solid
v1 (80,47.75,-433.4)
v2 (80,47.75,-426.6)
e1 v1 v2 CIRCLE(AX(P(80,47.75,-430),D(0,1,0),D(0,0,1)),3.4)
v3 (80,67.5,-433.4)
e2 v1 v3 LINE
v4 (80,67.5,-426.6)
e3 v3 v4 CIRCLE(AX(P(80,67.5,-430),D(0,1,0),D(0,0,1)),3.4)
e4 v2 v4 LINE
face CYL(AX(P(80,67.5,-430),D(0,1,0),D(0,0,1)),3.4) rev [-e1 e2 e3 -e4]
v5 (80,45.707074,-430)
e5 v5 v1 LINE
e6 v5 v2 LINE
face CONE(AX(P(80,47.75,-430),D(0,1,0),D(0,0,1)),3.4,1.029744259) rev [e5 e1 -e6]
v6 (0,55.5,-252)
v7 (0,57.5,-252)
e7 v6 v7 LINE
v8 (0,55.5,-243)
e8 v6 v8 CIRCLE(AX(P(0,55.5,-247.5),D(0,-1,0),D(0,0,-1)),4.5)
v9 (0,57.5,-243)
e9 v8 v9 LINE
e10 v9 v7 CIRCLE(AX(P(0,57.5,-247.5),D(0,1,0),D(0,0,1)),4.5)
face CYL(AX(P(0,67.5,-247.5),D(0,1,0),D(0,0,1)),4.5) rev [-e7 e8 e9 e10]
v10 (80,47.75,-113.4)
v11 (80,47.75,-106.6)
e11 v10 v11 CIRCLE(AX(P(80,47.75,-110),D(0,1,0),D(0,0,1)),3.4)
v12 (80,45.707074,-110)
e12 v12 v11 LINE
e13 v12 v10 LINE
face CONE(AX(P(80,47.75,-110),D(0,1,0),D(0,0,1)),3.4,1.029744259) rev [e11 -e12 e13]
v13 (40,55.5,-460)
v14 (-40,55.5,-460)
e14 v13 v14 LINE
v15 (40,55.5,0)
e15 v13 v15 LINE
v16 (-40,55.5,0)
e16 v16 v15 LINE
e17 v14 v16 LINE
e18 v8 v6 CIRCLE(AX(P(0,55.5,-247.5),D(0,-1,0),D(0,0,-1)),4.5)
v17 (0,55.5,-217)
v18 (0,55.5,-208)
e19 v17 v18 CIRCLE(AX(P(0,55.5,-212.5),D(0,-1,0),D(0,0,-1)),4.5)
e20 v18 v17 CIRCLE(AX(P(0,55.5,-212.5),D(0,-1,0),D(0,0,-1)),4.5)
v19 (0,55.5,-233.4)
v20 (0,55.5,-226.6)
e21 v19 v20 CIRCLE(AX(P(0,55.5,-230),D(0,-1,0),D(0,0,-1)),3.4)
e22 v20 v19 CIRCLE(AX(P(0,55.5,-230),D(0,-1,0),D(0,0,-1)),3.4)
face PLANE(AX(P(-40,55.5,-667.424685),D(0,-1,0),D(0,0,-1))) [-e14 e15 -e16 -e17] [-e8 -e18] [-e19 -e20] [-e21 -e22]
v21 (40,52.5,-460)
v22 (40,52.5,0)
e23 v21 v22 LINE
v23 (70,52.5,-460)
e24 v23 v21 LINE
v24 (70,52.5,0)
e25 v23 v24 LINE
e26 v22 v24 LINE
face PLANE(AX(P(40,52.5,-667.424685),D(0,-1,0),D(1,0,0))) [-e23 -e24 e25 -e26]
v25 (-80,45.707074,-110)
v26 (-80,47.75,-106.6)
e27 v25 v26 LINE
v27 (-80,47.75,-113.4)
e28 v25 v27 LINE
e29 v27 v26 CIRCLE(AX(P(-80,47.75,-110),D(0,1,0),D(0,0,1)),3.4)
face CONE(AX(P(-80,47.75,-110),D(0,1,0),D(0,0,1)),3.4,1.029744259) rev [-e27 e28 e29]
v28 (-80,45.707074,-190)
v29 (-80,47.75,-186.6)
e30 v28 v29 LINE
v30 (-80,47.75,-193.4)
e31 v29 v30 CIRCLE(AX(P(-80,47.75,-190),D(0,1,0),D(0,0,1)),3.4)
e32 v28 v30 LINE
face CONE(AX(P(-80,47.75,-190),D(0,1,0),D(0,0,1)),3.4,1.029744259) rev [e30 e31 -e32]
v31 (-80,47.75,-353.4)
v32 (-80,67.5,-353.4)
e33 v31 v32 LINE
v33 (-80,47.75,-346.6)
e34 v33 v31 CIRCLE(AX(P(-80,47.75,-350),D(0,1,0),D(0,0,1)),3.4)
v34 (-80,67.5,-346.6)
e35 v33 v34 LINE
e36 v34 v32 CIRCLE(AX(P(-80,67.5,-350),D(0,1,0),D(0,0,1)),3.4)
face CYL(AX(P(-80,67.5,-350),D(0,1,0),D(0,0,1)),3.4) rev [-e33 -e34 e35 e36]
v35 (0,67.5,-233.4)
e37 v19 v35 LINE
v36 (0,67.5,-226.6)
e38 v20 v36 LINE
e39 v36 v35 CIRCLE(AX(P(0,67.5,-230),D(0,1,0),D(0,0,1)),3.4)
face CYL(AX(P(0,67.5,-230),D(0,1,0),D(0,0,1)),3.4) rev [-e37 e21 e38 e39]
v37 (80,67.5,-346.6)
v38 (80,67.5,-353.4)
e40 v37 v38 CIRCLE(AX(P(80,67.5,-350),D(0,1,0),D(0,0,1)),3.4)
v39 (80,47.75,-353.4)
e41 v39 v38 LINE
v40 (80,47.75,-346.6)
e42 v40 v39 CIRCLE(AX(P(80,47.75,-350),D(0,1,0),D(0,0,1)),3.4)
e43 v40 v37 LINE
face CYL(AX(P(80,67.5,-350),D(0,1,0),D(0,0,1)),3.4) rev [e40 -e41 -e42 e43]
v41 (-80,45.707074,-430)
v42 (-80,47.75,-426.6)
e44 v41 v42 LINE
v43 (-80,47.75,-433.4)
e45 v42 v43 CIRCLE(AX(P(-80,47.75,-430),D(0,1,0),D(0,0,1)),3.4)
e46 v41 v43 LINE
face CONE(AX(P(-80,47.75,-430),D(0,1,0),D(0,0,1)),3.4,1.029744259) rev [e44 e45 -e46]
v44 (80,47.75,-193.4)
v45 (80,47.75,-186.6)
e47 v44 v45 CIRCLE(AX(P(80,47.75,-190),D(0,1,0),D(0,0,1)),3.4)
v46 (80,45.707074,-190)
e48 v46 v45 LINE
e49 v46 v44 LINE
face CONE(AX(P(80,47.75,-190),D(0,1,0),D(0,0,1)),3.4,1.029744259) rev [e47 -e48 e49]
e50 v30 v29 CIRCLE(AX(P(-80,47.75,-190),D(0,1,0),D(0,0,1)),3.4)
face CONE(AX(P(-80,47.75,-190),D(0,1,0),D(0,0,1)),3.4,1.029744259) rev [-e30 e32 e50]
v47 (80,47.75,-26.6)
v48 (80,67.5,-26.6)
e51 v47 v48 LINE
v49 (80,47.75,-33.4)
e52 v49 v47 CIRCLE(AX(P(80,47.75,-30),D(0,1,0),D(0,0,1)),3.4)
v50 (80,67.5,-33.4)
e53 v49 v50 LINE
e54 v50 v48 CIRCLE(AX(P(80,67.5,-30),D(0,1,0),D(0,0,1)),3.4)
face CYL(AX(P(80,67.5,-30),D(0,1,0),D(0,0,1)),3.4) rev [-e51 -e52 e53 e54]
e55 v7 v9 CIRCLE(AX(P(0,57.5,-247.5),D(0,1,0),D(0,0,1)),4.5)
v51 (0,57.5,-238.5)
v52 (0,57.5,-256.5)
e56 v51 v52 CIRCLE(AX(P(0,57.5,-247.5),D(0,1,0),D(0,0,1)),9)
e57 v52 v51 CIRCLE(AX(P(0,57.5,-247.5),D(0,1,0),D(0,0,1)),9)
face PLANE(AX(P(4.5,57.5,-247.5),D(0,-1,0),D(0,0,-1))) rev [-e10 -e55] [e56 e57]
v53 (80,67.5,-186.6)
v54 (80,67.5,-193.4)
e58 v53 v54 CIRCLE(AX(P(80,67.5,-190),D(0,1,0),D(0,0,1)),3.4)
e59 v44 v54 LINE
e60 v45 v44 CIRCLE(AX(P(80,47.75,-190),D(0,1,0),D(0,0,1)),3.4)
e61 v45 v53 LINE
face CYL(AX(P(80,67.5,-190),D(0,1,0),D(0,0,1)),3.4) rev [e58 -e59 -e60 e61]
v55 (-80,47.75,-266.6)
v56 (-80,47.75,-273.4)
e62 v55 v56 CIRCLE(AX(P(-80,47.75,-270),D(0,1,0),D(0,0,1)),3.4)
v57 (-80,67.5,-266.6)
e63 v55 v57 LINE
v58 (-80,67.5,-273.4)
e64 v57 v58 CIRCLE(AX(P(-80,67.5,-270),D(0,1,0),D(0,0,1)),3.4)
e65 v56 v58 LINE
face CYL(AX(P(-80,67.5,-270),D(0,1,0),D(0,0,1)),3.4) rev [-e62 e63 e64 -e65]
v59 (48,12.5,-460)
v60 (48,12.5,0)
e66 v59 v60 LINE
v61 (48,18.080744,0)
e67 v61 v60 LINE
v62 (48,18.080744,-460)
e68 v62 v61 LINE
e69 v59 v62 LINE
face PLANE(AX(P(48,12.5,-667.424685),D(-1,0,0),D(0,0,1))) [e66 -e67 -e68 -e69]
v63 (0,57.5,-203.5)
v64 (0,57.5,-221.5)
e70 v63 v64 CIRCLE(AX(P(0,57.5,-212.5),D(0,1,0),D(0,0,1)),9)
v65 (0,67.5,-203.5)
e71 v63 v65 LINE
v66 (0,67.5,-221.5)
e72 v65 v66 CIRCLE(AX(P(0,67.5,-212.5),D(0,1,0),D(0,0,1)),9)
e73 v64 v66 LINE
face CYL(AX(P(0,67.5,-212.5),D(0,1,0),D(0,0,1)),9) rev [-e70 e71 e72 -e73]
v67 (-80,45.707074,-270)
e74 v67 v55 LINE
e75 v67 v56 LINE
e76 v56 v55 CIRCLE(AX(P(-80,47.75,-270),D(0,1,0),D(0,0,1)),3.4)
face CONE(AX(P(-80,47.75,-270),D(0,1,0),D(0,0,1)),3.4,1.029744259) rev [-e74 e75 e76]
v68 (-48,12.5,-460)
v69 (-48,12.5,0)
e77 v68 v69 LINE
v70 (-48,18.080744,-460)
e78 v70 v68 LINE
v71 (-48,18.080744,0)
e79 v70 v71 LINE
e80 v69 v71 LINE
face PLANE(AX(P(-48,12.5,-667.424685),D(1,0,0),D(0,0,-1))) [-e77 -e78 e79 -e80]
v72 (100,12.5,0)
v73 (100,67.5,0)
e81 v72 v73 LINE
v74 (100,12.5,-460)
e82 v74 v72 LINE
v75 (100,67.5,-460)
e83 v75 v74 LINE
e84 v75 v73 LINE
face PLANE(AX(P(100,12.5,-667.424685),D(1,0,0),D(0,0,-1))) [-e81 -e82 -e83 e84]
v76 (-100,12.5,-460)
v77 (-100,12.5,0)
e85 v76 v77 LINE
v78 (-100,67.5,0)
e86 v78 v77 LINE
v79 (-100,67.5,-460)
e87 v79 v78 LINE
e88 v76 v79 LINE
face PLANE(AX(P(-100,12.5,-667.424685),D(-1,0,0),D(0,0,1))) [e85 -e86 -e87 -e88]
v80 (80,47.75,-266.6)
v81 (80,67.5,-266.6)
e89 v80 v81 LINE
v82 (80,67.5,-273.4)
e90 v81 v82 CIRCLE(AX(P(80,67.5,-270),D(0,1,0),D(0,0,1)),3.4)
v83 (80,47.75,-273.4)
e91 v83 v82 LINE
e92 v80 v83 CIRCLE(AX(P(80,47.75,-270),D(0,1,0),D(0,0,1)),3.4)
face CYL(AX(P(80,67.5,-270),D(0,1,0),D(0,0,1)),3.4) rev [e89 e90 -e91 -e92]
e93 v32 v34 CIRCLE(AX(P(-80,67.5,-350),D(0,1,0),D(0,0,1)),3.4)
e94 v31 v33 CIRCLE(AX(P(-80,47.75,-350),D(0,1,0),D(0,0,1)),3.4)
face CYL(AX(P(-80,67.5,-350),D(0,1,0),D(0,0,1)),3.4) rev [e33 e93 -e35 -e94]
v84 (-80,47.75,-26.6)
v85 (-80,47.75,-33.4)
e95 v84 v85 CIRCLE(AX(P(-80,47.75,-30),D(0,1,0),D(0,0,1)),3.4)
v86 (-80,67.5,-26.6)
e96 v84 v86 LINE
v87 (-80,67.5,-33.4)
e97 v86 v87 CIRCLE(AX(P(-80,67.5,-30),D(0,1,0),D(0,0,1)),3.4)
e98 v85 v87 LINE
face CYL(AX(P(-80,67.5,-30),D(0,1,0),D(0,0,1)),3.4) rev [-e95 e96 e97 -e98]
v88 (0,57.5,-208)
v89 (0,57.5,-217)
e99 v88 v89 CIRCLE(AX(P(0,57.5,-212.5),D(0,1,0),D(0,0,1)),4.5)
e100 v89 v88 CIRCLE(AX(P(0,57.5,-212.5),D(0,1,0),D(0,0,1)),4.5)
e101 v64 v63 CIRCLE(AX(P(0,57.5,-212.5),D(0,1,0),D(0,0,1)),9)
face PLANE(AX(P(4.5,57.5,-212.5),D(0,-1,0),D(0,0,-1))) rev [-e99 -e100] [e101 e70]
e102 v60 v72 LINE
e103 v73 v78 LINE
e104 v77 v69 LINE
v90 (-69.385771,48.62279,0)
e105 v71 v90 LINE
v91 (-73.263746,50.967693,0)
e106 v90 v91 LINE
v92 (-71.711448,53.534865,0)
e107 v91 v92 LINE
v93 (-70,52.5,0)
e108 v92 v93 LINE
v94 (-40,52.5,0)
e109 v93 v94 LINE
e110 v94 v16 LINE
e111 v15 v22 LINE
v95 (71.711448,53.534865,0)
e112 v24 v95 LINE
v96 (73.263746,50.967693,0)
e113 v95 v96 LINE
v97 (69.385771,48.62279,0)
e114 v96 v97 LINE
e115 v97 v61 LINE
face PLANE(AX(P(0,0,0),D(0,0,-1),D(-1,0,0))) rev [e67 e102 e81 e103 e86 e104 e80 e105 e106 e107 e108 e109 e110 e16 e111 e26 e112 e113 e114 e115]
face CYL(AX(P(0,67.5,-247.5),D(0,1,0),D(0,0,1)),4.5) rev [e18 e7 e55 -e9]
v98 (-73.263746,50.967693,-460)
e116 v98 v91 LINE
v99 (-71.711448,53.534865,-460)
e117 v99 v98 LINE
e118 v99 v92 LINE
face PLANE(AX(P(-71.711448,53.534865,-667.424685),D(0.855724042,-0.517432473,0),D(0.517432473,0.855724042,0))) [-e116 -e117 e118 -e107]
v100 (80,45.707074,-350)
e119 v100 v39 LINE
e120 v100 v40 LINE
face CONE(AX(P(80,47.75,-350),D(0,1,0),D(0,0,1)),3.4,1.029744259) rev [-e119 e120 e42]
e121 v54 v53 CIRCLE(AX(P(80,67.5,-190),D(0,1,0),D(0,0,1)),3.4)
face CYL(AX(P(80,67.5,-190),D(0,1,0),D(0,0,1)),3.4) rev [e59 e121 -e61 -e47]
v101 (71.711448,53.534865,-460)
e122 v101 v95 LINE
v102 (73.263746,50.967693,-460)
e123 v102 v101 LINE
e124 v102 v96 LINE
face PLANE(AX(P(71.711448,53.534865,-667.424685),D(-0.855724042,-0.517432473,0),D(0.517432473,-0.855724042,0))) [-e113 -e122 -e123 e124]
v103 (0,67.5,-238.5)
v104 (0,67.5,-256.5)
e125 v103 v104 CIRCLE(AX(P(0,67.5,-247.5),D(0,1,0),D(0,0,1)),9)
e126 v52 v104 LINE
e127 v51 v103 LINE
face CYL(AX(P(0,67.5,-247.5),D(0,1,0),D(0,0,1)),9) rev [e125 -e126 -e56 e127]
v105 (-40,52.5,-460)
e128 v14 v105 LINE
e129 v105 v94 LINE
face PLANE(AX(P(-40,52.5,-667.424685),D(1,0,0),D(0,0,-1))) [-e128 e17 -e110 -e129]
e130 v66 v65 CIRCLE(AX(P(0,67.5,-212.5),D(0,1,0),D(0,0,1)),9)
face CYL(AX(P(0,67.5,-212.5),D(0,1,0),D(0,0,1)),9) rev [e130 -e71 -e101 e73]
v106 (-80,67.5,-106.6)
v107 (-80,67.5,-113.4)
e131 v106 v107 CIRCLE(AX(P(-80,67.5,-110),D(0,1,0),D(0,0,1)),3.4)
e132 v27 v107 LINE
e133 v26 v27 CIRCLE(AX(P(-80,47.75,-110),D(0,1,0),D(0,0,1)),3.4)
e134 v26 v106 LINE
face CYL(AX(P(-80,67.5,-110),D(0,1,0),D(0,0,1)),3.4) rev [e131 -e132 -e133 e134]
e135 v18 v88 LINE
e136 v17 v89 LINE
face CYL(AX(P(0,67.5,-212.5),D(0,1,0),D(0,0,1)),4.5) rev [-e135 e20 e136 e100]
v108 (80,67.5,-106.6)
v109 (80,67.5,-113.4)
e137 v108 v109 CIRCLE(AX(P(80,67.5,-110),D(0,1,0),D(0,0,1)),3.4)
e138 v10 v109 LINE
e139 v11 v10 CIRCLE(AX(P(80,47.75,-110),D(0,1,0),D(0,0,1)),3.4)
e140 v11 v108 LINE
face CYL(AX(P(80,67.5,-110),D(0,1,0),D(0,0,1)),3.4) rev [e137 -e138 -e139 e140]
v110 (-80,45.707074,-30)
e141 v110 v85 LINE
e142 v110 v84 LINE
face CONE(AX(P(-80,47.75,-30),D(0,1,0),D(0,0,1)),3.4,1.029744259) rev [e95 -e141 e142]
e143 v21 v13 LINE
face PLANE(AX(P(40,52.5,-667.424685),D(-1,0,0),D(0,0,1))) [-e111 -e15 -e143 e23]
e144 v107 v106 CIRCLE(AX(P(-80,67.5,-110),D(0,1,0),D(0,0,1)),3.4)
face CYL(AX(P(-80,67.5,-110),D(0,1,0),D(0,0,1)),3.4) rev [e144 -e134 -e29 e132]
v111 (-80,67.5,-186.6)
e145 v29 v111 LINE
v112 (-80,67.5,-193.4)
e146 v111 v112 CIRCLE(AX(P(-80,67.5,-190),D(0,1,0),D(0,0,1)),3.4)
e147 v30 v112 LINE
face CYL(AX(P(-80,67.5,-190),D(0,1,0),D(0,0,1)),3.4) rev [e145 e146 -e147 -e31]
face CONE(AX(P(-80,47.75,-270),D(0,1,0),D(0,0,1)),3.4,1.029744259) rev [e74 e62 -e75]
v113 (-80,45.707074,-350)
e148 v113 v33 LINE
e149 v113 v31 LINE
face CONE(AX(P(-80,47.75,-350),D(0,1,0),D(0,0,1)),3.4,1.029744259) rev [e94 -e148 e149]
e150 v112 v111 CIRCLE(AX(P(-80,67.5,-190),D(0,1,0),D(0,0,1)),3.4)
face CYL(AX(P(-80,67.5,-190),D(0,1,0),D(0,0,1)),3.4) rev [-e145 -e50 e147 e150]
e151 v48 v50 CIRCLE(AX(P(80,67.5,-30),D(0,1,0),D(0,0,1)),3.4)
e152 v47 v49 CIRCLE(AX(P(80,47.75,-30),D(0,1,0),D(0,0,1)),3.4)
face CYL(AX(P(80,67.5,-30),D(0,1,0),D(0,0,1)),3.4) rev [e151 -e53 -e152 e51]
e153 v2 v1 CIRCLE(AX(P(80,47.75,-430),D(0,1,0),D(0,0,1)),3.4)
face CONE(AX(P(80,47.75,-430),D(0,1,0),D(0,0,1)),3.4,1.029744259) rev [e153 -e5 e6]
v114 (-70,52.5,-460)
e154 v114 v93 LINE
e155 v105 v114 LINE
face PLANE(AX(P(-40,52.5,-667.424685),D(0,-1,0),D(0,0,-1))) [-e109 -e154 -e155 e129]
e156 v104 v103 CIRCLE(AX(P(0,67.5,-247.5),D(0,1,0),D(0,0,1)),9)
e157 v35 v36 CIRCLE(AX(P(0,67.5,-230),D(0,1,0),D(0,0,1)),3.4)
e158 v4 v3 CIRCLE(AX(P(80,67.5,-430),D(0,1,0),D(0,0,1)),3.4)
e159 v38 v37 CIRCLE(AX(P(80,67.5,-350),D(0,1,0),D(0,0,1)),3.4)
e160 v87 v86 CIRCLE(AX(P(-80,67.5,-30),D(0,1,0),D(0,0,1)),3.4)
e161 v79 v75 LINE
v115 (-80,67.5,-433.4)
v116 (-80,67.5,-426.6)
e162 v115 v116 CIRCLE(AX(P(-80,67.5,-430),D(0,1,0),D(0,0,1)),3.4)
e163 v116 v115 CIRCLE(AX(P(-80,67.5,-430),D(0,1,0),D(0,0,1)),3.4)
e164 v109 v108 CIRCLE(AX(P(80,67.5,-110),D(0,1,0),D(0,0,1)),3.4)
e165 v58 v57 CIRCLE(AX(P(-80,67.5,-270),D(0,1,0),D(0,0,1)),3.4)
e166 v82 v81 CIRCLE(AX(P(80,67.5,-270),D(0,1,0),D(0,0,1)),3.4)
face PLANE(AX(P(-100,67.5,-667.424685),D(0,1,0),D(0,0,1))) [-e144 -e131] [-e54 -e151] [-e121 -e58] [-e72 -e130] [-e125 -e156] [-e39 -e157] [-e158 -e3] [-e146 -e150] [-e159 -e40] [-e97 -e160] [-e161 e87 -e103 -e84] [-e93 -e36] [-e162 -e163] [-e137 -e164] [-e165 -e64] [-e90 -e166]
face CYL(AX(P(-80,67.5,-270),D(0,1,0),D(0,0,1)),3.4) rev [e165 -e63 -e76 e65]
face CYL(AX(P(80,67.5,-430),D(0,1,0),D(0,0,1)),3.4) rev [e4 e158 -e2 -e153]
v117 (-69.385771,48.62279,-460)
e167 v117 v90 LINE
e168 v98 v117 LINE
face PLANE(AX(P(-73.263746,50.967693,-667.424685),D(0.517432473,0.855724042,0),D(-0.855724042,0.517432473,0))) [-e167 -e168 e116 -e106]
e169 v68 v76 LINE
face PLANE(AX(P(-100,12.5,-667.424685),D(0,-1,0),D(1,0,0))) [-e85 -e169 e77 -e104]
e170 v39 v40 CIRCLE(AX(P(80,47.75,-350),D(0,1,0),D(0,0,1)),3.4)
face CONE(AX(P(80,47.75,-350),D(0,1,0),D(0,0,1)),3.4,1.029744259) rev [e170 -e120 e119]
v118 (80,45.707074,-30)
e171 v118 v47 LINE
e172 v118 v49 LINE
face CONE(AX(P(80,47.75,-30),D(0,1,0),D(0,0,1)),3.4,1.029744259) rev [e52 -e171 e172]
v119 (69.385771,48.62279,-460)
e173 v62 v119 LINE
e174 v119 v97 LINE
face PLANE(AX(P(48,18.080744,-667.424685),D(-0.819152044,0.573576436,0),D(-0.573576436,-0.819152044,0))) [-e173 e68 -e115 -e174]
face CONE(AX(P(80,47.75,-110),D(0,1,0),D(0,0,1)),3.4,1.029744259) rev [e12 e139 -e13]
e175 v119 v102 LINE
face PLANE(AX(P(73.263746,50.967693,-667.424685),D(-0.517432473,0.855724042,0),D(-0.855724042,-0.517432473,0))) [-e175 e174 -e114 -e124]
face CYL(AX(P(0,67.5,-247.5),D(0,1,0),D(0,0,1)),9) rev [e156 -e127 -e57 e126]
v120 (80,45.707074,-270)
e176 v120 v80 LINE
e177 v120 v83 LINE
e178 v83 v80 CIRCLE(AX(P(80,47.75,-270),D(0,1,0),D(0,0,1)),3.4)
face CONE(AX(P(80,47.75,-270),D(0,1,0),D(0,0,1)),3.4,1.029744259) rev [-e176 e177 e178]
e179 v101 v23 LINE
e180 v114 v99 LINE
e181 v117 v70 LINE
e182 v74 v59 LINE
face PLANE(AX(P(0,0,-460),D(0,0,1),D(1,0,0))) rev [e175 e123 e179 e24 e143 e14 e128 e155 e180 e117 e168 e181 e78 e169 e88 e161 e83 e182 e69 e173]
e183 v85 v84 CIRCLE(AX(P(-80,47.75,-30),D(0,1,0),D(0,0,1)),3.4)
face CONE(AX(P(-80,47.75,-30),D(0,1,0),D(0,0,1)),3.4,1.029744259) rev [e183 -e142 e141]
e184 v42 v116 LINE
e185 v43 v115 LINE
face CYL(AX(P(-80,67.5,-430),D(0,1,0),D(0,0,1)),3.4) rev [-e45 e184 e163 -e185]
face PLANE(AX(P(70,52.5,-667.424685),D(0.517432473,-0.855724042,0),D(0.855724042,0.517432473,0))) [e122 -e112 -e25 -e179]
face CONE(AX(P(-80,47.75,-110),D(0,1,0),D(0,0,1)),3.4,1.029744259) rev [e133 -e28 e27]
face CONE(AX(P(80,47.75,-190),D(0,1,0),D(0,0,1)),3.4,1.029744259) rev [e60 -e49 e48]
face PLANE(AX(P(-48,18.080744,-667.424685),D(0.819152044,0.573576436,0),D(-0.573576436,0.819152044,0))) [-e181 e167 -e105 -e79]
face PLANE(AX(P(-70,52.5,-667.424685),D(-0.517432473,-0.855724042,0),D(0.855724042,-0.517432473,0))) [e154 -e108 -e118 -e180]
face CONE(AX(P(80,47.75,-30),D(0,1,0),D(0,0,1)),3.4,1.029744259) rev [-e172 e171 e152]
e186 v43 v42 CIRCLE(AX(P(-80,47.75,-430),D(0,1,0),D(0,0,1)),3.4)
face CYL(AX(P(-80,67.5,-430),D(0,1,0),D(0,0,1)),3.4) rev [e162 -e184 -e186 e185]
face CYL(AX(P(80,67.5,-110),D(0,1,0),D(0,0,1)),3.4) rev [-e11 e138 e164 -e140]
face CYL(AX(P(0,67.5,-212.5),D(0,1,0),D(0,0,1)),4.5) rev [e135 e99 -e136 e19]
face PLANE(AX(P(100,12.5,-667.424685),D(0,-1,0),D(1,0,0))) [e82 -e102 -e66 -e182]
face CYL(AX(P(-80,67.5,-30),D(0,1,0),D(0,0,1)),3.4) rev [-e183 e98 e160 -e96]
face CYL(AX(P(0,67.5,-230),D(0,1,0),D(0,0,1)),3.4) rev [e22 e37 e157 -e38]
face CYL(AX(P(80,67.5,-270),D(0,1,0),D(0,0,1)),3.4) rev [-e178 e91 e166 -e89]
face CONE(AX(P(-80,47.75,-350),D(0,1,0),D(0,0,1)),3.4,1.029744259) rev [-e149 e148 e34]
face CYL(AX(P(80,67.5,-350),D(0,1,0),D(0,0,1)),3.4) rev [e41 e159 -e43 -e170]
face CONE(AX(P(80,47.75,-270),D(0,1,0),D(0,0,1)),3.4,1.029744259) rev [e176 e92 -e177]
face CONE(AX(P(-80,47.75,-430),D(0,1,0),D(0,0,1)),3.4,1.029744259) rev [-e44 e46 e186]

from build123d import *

# Parameters (mm, degrees)
BOSS_EXTRUDE1_DEPTH                     = 460
CBORE_FOR_M8_HEX_HEAD_BOLT1_D           = 9
CBORE_FOR_M8_HEX_HEAD_BOLT1_CBORE_D     = 18
CBORE_FOR_M8_HEX_HEAD_BOLT1_CBORE_DEPTH = 10
M8_TAPPED_HOLE1_D                       = 6.8
M8_TAPPED_HOLE1_DEPTH                   = 19.75
M8_TAPPED_HOLE1_TIP                     = 2.042926105


with BuildPart() as part:
    # Sketch1 → Boss-Extrude1 (new body)
    with BuildSketch(Plane.XY):
        Polygon((-40, 52.5), (-40, 55.5), (40, 55.5), (40, 52.5), (70, 52.5), (71.711448084, 53.534864946), (73.263745503, 50.96769282), (69.385770597, 48.622789502), (48, 18.080743852), (48, 12.5), (100, 12.5), (100, 67.5), (-100, 67.5), (-100, 12.5), (-48, 12.5), (-48, 18.080743852), (-69.385770597, 48.622789502), (-73.263745503, 50.96769282), (-71.711448084, 53.534864946), (-70, 52.5), align=None)
    extrude(amount=-BOSS_EXTRUDE1_DEPTH)

    # CBORE for M8 Hex Head Bolt1 (through all)
    with Locations(Plane(origin=(0, 67.5, 0), x_dir=(1, 0, 0), z_dir=(0, 1, 0))):
        with Locations((0, 247.5), (0, 212.5)):
            CounterBoreHole(CBORE_FOR_M8_HEX_HEAD_BOLT1_D / 2, CBORE_FOR_M8_HEX_HEAD_BOLT1_CBORE_D / 2, CBORE_FOR_M8_HEX_HEAD_BOLT1_CBORE_DEPTH)

    # M8 Tapped Hole1
    with Locations(Plane(origin=(0, 67.5, 0), x_dir=(1, 0, 0), z_dir=(0, 1, 0))):
        with Locations((1.4e-07, 230), (80.000000279, 430), (-80, 30), (-80, 430), (80.000000279, 30), (-80, 350), (80.000000279, 350), (-80, 270), (80.000000279, 270), (-80, 190), (80.000000279, 190), (-80, 110), (80.000000279, 110)):
            Hole(M8_TAPPED_HOLE1_D / 2, depth=M8_TAPPED_HOLE1_DEPTH)
            with Locations((0, 0, -(M8_TAPPED_HOLE1_DEPTH + M8_TAPPED_HOLE1_TIP / 2))):  # 118° drill point
                Cone(0, M8_TAPPED_HOLE1_D / 2, M8_TAPPED_HOLE1_TIP, mode=Mode.SUBTRACT)


solid = part.part
